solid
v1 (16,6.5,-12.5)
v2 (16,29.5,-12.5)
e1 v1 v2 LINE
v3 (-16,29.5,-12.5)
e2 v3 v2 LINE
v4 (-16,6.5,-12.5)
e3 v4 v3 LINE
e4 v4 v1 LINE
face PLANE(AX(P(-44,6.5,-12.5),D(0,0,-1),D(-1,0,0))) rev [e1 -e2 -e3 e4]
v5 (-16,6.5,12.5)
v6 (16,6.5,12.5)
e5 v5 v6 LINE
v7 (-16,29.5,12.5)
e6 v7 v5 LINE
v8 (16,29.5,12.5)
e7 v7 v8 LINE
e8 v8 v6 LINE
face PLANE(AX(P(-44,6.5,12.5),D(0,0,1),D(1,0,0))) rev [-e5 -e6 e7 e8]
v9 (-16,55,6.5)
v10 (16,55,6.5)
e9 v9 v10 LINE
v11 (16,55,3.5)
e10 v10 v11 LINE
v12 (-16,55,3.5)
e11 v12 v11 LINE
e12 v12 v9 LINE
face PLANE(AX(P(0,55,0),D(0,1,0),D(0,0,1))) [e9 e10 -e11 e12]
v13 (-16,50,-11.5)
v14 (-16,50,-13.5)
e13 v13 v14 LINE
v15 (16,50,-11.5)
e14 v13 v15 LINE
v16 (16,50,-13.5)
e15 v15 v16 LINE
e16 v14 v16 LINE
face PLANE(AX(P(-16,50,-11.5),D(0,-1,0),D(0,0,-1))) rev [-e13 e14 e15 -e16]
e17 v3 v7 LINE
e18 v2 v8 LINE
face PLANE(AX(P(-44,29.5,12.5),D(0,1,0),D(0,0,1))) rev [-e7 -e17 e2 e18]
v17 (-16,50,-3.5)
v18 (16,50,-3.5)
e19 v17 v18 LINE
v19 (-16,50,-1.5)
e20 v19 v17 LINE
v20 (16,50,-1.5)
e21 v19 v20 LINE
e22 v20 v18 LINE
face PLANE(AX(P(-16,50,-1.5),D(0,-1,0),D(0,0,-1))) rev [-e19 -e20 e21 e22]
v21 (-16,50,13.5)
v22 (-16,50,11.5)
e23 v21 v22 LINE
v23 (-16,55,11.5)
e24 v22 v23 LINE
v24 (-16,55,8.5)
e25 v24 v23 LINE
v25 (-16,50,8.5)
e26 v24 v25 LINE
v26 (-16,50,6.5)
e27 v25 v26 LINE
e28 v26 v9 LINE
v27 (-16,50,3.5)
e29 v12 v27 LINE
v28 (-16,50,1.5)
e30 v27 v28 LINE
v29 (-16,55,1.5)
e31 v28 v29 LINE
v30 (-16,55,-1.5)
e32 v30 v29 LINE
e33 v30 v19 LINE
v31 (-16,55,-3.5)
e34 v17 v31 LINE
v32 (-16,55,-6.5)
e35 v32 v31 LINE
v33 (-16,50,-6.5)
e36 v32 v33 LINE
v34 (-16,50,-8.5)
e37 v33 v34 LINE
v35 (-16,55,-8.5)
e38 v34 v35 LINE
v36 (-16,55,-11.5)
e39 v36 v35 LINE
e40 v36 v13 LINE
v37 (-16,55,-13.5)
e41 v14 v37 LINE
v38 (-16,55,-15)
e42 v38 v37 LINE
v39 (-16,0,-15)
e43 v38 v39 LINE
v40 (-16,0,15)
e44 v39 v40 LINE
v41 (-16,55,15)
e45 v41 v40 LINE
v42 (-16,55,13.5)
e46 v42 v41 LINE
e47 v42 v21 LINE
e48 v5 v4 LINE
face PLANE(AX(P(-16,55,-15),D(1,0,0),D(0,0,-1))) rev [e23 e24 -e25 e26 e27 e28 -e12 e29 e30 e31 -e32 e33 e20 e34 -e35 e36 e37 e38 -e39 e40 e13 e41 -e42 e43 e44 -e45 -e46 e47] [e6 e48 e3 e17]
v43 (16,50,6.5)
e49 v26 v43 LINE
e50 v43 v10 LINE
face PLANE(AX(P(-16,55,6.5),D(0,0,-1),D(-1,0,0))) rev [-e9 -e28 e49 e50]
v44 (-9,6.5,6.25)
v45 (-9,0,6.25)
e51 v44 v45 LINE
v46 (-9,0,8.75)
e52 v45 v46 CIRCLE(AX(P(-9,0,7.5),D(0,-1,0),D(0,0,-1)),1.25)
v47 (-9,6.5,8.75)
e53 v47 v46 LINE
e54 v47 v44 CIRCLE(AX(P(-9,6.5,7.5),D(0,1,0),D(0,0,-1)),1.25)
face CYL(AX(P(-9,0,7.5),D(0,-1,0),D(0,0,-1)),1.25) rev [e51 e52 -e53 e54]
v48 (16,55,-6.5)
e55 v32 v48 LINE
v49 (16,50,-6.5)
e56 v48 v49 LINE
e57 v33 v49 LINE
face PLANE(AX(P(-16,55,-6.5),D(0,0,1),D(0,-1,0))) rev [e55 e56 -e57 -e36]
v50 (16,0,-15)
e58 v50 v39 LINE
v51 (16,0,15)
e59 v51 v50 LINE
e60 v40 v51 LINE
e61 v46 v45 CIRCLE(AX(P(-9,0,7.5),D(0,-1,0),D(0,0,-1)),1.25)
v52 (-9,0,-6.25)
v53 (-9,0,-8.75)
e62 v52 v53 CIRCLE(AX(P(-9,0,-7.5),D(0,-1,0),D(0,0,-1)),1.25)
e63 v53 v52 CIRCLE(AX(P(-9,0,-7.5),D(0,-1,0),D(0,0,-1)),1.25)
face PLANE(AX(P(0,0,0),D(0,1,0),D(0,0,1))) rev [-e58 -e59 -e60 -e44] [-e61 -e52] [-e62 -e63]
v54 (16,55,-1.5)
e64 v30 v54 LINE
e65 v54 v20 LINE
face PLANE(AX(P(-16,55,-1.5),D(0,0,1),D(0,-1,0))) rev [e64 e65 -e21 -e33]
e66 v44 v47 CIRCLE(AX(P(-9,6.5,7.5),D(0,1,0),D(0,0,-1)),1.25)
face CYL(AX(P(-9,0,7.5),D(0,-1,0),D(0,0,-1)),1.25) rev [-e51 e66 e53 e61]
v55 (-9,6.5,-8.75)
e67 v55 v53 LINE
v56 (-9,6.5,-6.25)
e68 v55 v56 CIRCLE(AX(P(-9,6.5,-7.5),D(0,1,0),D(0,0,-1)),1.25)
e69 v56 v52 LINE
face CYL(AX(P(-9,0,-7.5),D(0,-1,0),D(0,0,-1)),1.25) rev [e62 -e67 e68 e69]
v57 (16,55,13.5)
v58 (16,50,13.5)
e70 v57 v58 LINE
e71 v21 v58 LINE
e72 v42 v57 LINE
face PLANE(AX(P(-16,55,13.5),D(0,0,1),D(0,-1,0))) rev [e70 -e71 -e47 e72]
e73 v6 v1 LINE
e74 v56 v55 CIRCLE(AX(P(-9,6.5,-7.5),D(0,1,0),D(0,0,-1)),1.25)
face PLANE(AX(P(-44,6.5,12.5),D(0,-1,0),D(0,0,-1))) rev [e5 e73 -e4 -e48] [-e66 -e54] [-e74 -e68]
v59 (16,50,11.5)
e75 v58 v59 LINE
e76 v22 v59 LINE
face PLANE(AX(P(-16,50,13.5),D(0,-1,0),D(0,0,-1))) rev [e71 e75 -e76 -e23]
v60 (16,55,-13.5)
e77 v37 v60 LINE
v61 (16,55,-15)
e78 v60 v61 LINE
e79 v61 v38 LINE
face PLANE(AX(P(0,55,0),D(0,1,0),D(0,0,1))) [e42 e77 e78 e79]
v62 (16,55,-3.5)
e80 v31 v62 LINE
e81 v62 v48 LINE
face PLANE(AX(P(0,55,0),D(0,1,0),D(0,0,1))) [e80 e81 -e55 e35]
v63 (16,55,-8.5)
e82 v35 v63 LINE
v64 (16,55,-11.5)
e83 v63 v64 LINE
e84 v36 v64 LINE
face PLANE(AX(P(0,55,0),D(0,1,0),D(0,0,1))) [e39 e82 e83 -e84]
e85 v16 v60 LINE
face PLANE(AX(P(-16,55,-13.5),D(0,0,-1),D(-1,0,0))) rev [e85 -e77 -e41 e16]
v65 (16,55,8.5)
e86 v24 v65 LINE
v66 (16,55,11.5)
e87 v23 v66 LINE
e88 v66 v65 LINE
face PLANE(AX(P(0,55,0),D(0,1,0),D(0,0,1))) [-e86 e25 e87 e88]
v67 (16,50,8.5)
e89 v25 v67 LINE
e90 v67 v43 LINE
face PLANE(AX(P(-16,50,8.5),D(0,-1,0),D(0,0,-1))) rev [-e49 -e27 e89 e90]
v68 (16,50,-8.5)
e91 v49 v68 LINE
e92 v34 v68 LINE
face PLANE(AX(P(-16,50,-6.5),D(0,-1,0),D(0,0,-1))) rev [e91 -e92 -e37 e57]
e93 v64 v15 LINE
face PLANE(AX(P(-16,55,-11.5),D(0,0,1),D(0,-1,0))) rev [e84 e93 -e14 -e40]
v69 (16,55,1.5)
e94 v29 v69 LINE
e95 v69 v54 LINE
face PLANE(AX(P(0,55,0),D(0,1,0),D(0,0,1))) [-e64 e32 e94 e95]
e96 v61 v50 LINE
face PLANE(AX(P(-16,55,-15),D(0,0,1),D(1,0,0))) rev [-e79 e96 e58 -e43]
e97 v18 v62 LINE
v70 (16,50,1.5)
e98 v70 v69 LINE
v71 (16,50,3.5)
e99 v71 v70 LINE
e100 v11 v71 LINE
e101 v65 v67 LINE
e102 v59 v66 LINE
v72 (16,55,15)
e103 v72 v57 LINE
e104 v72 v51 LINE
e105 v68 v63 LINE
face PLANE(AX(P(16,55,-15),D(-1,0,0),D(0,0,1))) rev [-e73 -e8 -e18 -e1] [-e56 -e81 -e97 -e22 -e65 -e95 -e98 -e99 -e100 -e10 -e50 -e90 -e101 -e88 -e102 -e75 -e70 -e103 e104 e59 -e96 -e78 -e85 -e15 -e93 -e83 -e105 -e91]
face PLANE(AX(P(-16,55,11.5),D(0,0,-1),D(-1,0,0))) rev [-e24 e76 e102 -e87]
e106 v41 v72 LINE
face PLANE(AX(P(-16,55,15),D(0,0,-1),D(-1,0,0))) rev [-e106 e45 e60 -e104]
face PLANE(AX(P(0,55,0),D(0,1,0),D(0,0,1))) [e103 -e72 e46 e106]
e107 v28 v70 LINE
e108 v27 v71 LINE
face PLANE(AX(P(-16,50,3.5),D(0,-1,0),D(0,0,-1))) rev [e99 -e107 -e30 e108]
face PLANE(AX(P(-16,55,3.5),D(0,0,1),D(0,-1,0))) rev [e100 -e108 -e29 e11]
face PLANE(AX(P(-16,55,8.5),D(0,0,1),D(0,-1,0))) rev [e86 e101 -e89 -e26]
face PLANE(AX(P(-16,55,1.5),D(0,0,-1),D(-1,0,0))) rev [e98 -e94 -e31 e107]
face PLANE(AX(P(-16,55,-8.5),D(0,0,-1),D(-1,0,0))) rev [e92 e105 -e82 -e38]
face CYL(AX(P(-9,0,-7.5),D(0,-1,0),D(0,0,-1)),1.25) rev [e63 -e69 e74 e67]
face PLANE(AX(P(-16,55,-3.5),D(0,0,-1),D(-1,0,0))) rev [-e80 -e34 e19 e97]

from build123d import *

# Parameters (mm, degrees)
SKETCH_1_W             = 32
SKETCH_1_H             = 30
EXTRUDE_1_DEPTH        = 55
HOLE_WIZARD_M3_1_D     = 2.5
HOLE_WIZARD_M3_1_DEPTH = 7.5
HOLE_WIZARD_M3_1_TIP   = 0.751075774
SKETCH_5_W             = 25
SKETCH_5_H             = 23
CUT_EXTRUDE_2_DEPTH    = 60
SKETCH_6_W             = 2
SKETCH_6_H             = 5
CUT_EXTRUDE_3_DEPTH    = 66.375836515
PATTERN_LINEAR_1_COUNT = 6
PATTERN_LINEAR_1_PITCH = 5


with BuildPart() as part:
    # 草图1 → 凸台-拉伸1 (new body)
    with BuildSketch(Plane(origin=(0, 0, 0), x_dir=(1, 0, 0), z_dir=(0, 1, 0))):
        Rectangle(SKETCH_1_W, SKETCH_1_H)
    extrude(amount=EXTRUDE_1_DEPTH)

    # M3 螺纹孔1
    with Locations(Plane(origin=(0, 0, 0), x_dir=(-1, 0, 0), z_dir=(0, -1, 0))):
        with Locations((9, 7.5), (9, -7.5)):
            Hole(HOLE_WIZARD_M3_1_D / 2, depth=HOLE_WIZARD_M3_1_DEPTH)
            with Locations((0, 0, -(HOLE_WIZARD_M3_1_DEPTH + HOLE_WIZARD_M3_1_TIP / 2))):  # 118° drill point
                Cone(0, HOLE_WIZARD_M3_1_D / 2, HOLE_WIZARD_M3_1_TIP, mode=Mode.SUBTRACT)

    # 草图5 → 切除-拉伸2 (cut)
    with BuildSketch(Plane(origin=(16, 0, 0), x_dir=(0, 0, -1), z_dir=(1, 0, 0))):
        with Locations((0, 18)):
            Rectangle(SKETCH_5_W, SKETCH_5_H)
    extrude(amount=-CUT_EXTRUDE_2_DEPTH, mode=Mode.SUBTRACT)

    # 草图6 → 切除-拉伸3 (cut, through all)
    with BuildSketch(Plane(origin=(16, 0, 0), x_dir=(0, 0, -1), z_dir=(1, 0, 0))):
        with Locations((-12.5, 52.5)):
            Rectangle(SKETCH_6_W, SKETCH_6_H)
    cut_extrude_3 = extrude(amount=-CUT_EXTRUDE_3_DEPTH, mode=Mode.SUBTRACT)

    # 阵列(线性)1: 切除-拉伸3 ×6
    with Locations(*[(0, 0, -i * PATTERN_LINEAR_1_PITCH) for i in range(1, PATTERN_LINEAR_1_COUNT)]):
        add(cut_extrude_3, mode=Mode.SUBTRACT)


solid = part.part
